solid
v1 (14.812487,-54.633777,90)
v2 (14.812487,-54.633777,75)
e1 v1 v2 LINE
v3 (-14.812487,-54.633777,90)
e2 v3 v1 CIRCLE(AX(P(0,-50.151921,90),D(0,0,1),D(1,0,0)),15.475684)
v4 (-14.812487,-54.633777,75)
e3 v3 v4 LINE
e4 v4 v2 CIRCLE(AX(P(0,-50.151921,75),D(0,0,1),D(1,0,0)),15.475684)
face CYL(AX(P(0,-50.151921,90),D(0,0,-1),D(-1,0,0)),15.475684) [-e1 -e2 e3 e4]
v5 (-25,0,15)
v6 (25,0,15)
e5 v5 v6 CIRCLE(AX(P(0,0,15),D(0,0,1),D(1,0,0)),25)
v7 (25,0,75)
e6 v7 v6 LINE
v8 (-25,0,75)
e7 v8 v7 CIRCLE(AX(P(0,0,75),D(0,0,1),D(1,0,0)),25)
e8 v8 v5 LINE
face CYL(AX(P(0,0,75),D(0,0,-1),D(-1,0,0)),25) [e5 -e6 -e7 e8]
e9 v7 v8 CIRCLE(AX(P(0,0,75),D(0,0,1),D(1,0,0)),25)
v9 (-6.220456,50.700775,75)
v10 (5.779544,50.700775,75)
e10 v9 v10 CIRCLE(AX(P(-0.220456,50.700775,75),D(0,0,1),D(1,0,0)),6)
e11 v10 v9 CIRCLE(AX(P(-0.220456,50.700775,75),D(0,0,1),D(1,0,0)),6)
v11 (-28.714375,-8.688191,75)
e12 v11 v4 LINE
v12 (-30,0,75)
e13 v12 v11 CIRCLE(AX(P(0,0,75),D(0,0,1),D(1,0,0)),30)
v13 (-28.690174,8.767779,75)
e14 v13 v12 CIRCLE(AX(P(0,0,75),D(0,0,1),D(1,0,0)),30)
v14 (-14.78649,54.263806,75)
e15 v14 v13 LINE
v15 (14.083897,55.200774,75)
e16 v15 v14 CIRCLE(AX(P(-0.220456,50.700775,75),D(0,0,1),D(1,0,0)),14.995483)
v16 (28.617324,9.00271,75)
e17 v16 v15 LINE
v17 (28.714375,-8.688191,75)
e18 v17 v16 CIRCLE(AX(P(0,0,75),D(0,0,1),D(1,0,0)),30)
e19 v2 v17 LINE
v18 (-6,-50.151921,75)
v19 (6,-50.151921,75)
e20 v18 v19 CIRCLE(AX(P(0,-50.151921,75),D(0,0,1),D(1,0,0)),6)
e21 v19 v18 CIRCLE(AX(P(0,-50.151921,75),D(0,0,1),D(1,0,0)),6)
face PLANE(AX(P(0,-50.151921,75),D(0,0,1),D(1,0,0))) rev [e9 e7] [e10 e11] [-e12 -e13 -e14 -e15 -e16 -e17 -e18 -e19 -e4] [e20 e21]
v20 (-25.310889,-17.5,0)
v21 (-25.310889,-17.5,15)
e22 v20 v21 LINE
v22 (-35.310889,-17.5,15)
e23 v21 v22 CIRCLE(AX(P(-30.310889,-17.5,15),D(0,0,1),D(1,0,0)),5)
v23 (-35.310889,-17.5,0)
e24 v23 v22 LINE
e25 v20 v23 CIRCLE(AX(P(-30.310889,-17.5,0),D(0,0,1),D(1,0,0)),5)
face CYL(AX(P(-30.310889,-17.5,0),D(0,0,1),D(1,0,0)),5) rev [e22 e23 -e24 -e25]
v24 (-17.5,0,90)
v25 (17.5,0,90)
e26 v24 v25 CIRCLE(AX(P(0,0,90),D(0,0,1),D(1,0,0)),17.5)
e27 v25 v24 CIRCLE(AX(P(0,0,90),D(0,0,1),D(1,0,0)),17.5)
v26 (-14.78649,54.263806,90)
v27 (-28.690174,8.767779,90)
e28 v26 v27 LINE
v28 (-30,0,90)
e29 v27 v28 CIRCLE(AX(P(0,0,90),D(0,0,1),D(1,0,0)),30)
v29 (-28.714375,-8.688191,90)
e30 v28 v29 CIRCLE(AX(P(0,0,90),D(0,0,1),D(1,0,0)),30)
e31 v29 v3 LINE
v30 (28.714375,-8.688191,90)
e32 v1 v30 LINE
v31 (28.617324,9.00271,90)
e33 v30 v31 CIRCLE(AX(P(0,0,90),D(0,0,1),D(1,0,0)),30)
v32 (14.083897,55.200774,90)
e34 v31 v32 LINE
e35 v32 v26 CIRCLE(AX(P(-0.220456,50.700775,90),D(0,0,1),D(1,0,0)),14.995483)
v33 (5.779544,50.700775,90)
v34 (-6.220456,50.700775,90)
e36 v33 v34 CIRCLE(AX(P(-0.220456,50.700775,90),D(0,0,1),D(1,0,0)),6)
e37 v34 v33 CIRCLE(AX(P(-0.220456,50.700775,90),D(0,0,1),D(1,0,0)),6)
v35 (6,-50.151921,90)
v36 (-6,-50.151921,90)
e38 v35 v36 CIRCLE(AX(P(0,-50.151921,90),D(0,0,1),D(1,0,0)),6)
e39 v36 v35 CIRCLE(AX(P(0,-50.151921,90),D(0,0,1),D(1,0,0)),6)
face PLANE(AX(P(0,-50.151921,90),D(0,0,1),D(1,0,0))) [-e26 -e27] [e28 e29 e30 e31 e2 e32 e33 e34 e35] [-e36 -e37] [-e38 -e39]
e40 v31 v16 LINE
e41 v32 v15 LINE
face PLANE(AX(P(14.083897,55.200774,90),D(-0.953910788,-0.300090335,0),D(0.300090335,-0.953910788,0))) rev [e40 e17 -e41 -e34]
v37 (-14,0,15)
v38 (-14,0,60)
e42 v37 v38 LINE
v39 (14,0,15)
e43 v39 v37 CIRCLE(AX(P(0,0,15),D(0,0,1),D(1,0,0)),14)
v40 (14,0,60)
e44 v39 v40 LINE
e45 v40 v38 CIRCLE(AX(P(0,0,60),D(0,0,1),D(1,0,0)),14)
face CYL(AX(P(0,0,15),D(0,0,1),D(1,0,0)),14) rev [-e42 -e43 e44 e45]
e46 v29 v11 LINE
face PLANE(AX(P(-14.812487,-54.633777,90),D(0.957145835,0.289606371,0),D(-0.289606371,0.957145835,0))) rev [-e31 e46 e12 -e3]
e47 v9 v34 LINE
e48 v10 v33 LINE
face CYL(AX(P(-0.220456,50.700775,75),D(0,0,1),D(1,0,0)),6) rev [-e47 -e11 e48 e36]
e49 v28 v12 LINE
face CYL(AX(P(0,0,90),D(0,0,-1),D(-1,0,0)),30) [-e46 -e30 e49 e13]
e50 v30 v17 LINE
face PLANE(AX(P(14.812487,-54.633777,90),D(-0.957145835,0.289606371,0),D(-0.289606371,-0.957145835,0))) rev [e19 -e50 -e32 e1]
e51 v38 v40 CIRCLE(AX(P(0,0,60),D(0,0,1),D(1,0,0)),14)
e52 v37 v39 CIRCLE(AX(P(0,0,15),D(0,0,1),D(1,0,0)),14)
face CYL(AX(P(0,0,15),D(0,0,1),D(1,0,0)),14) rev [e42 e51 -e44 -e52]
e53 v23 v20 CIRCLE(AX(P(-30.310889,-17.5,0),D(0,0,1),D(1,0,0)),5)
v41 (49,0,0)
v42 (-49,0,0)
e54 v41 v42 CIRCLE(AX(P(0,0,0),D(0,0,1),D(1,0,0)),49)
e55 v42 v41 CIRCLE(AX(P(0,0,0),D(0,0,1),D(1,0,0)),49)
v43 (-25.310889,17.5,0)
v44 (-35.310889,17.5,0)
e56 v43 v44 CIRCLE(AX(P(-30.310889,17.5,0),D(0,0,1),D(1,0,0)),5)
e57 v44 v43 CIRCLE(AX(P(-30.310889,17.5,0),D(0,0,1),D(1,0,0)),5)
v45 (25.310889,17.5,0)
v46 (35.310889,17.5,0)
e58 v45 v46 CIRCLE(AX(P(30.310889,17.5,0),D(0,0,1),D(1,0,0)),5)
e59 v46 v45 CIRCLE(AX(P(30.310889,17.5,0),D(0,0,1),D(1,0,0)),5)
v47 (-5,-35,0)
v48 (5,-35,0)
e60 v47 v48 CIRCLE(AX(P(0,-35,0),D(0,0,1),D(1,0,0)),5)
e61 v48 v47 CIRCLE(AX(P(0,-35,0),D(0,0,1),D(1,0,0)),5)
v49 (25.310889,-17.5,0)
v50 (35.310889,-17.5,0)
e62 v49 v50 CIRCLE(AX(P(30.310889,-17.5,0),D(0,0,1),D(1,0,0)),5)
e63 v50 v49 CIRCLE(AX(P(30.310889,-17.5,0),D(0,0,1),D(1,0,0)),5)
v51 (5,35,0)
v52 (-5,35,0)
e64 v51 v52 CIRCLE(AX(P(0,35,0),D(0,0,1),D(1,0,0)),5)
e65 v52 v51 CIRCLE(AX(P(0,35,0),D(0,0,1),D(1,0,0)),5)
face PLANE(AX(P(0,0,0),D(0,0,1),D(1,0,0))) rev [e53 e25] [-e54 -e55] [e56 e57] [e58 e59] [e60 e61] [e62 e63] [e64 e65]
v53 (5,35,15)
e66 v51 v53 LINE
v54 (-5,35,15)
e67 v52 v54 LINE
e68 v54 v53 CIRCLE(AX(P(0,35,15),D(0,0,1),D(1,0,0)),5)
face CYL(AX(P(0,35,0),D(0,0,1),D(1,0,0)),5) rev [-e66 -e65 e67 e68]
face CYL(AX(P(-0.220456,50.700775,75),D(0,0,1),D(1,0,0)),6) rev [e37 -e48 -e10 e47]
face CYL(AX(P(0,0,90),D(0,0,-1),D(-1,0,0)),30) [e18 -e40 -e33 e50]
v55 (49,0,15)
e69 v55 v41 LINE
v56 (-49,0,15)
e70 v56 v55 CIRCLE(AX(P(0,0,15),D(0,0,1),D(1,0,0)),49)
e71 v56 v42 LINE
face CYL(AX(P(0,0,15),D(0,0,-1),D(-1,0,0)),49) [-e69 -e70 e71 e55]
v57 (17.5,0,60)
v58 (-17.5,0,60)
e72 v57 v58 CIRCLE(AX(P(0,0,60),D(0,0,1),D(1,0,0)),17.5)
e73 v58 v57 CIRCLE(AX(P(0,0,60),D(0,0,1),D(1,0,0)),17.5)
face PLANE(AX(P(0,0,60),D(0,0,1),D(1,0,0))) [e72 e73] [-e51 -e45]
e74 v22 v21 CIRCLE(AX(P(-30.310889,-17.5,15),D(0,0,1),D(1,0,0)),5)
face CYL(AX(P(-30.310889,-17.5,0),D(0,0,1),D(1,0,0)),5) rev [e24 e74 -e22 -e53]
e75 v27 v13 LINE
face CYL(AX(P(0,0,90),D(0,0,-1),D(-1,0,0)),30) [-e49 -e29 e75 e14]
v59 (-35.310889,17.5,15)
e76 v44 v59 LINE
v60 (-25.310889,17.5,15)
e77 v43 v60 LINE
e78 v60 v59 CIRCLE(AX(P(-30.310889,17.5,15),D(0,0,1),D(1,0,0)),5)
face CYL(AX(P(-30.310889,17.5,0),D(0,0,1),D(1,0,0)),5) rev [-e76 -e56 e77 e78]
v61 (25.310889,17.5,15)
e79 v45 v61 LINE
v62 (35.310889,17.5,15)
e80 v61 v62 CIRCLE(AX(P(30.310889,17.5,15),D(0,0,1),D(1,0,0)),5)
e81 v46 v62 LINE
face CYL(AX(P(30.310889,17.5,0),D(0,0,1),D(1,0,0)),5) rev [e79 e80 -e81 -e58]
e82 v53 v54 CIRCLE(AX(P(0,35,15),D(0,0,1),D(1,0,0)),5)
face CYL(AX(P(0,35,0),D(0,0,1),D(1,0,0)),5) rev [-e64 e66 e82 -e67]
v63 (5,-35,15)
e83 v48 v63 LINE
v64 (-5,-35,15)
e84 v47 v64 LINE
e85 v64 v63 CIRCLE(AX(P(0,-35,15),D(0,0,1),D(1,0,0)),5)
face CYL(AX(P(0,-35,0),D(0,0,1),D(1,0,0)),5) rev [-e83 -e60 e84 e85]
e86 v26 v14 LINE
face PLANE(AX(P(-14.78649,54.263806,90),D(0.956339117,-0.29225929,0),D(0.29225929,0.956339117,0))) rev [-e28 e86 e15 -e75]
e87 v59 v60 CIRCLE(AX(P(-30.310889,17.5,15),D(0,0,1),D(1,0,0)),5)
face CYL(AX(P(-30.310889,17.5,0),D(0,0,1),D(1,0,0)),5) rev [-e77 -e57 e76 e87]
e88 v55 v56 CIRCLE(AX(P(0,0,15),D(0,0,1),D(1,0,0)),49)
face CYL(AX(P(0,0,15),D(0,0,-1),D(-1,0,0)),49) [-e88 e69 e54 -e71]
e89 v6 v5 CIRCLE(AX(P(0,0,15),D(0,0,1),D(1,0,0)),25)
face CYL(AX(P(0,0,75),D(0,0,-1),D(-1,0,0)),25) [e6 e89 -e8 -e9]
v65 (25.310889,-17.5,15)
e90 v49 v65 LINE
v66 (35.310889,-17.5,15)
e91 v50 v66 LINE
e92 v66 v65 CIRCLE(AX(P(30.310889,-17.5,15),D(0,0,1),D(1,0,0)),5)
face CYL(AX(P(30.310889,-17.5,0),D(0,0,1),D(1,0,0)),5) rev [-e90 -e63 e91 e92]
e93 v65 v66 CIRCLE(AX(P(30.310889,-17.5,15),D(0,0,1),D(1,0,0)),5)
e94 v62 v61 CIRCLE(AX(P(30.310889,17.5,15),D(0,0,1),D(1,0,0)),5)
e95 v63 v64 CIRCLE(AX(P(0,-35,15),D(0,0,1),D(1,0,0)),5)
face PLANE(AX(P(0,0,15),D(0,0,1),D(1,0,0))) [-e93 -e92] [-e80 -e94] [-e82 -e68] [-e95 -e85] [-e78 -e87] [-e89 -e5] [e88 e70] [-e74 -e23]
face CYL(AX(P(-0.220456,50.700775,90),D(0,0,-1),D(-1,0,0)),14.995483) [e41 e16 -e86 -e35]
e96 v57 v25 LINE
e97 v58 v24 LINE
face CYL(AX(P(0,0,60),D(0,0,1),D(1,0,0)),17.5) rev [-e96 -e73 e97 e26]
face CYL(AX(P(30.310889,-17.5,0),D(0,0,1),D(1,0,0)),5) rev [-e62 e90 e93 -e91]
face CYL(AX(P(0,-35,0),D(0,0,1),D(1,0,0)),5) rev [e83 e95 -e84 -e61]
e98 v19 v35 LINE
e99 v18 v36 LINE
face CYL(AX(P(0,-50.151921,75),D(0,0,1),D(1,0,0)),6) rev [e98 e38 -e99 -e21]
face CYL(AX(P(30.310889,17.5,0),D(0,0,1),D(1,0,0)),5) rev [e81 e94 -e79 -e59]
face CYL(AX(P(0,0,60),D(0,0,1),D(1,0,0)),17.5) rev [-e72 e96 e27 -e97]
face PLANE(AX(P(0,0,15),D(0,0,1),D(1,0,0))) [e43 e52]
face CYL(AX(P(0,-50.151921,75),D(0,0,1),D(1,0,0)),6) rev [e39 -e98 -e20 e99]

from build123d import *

# Parameters (mm, degrees)
ROUND_FLANGE_SKETCH_R          = 49
ROUND_FLANGE_98_DEPTH          = 15
ROUND_FLANGE_HOLES_SKETCH_R    = 5
ROUND_FLANGE_HOLES_6X_10_DEPTH = 15
SLEEVE_SKETCH_R                = 25
SLEEVE_50_DEPTH                = 60
OVAL_FLANGE_DEPTH              = 15
OVAL_FLANGE_HOLES_SKETCH_R     = 6
OVAL_FLANGE_HOLES_2X_12_DEPTH  = 15
COUNTERBORE_SKETCH_R           = 17.5
COUNTERBORE_35_DEPTH           = 30
BORE_SKETCH_R                  = 14
BORE_28_DEPTH                  = 45


with BuildPart() as part:
    # Round Flange Sketch → Round Flange Ø98 (new body)
    with BuildSketch(Plane.XY):
        Circle(ROUND_FLANGE_SKETCH_R)
    extrude(amount=ROUND_FLANGE_98_DEPTH)

    # Round Flange Holes Sketch → Round Flange Holes 6xØ10 (cut)
    with BuildSketch(Plane.XY.offset(15)):
        with Locations((0, 35)):
            Circle(ROUND_FLANGE_HOLES_SKETCH_R)
        with Locations((30.310889132, 17.5)):
            Circle(ROUND_FLANGE_HOLES_SKETCH_R)
        with Locations((30.310889132, -17.5)):
            Circle(ROUND_FLANGE_HOLES_SKETCH_R)
        with Locations((0, -35)):
            Circle(ROUND_FLANGE_HOLES_SKETCH_R)
        with Locations((-30.310889132, -17.5)):
            Circle(ROUND_FLANGE_HOLES_SKETCH_R)
        with Locations((-30.310889132, 17.5)):
            Circle(ROUND_FLANGE_HOLES_SKETCH_R)
    extrude(amount=-ROUND_FLANGE_HOLES_6X_10_DEPTH, mode=Mode.SUBTRACT)

    # Sleeve Sketch → Sleeve Ø50 (add)
    with BuildSketch(Plane.XY.offset(15)):
        Circle(SLEEVE_SKETCH_R)
    extrude(amount=SLEEVE_50_DEPTH)

    # Oval Flange Sketch → Oval Flange (add)
    with BuildSketch(Plane.XY.offset(75)):
        with BuildLine():
            Line((-14.812486777, -54.633777367), (-28.714375061, -8.688191115))
            ThreePointArc((-28.714375061, -8.688191115), (-29.999971167, 0.041592963), (-28.690173521, 8.7677787))
            Line((-28.690173521, 8.7677787), (-14.786489776, 54.263806016))
            ThreePointArc((-14.786489776, 54.263806016), (-0.706868372, 65.68836713), (14.083896835, 55.200774455))
            Line((14.083896835, 55.200774455), (28.617323634, 9.002710037))
            ThreePointArc((28.617323634, 9.002710037), (29.999548575, 0.16457607), (28.714375061, -8.688191115))
            Line((28.714375061, -8.688191115), (14.812486777, -54.633777367))
            ThreePointArc((14.812486777, -54.633777367), (0, -65.627604906), (-14.812486777, -54.633777367))
        make_face()
    extrude(amount=OVAL_FLANGE_DEPTH)

    # Oval Flange Holes Sketch → Oval Flange Holes 2xØ12 (cut)
    with BuildSketch(Plane.XY.offset(90)):
        with Locations((-0.220456426, 50.700774863)):
            Circle(OVAL_FLANGE_HOLES_SKETCH_R)
        with Locations((0, -50.151920606)):
            Circle(OVAL_FLANGE_HOLES_SKETCH_R)
    extrude(amount=-OVAL_FLANGE_HOLES_2X_12_DEPTH, mode=Mode.SUBTRACT)

    # Counterbore Sketch → Counterbore Ø35 (cut)
    with BuildSketch(Plane.XY.offset(90)):
        Circle(COUNTERBORE_SKETCH_R)
    extrude(amount=-COUNTERBORE_35_DEPTH, mode=Mode.SUBTRACT)

    # Bore Sketch → Bore Ø28 (cut)
    with BuildSketch(Plane.XY.offset(60)):
        Circle(BORE_SKETCH_R)
    extrude(amount=-BORE_28_DEPTH, mode=Mode.SUBTRACT)


solid = part.part
